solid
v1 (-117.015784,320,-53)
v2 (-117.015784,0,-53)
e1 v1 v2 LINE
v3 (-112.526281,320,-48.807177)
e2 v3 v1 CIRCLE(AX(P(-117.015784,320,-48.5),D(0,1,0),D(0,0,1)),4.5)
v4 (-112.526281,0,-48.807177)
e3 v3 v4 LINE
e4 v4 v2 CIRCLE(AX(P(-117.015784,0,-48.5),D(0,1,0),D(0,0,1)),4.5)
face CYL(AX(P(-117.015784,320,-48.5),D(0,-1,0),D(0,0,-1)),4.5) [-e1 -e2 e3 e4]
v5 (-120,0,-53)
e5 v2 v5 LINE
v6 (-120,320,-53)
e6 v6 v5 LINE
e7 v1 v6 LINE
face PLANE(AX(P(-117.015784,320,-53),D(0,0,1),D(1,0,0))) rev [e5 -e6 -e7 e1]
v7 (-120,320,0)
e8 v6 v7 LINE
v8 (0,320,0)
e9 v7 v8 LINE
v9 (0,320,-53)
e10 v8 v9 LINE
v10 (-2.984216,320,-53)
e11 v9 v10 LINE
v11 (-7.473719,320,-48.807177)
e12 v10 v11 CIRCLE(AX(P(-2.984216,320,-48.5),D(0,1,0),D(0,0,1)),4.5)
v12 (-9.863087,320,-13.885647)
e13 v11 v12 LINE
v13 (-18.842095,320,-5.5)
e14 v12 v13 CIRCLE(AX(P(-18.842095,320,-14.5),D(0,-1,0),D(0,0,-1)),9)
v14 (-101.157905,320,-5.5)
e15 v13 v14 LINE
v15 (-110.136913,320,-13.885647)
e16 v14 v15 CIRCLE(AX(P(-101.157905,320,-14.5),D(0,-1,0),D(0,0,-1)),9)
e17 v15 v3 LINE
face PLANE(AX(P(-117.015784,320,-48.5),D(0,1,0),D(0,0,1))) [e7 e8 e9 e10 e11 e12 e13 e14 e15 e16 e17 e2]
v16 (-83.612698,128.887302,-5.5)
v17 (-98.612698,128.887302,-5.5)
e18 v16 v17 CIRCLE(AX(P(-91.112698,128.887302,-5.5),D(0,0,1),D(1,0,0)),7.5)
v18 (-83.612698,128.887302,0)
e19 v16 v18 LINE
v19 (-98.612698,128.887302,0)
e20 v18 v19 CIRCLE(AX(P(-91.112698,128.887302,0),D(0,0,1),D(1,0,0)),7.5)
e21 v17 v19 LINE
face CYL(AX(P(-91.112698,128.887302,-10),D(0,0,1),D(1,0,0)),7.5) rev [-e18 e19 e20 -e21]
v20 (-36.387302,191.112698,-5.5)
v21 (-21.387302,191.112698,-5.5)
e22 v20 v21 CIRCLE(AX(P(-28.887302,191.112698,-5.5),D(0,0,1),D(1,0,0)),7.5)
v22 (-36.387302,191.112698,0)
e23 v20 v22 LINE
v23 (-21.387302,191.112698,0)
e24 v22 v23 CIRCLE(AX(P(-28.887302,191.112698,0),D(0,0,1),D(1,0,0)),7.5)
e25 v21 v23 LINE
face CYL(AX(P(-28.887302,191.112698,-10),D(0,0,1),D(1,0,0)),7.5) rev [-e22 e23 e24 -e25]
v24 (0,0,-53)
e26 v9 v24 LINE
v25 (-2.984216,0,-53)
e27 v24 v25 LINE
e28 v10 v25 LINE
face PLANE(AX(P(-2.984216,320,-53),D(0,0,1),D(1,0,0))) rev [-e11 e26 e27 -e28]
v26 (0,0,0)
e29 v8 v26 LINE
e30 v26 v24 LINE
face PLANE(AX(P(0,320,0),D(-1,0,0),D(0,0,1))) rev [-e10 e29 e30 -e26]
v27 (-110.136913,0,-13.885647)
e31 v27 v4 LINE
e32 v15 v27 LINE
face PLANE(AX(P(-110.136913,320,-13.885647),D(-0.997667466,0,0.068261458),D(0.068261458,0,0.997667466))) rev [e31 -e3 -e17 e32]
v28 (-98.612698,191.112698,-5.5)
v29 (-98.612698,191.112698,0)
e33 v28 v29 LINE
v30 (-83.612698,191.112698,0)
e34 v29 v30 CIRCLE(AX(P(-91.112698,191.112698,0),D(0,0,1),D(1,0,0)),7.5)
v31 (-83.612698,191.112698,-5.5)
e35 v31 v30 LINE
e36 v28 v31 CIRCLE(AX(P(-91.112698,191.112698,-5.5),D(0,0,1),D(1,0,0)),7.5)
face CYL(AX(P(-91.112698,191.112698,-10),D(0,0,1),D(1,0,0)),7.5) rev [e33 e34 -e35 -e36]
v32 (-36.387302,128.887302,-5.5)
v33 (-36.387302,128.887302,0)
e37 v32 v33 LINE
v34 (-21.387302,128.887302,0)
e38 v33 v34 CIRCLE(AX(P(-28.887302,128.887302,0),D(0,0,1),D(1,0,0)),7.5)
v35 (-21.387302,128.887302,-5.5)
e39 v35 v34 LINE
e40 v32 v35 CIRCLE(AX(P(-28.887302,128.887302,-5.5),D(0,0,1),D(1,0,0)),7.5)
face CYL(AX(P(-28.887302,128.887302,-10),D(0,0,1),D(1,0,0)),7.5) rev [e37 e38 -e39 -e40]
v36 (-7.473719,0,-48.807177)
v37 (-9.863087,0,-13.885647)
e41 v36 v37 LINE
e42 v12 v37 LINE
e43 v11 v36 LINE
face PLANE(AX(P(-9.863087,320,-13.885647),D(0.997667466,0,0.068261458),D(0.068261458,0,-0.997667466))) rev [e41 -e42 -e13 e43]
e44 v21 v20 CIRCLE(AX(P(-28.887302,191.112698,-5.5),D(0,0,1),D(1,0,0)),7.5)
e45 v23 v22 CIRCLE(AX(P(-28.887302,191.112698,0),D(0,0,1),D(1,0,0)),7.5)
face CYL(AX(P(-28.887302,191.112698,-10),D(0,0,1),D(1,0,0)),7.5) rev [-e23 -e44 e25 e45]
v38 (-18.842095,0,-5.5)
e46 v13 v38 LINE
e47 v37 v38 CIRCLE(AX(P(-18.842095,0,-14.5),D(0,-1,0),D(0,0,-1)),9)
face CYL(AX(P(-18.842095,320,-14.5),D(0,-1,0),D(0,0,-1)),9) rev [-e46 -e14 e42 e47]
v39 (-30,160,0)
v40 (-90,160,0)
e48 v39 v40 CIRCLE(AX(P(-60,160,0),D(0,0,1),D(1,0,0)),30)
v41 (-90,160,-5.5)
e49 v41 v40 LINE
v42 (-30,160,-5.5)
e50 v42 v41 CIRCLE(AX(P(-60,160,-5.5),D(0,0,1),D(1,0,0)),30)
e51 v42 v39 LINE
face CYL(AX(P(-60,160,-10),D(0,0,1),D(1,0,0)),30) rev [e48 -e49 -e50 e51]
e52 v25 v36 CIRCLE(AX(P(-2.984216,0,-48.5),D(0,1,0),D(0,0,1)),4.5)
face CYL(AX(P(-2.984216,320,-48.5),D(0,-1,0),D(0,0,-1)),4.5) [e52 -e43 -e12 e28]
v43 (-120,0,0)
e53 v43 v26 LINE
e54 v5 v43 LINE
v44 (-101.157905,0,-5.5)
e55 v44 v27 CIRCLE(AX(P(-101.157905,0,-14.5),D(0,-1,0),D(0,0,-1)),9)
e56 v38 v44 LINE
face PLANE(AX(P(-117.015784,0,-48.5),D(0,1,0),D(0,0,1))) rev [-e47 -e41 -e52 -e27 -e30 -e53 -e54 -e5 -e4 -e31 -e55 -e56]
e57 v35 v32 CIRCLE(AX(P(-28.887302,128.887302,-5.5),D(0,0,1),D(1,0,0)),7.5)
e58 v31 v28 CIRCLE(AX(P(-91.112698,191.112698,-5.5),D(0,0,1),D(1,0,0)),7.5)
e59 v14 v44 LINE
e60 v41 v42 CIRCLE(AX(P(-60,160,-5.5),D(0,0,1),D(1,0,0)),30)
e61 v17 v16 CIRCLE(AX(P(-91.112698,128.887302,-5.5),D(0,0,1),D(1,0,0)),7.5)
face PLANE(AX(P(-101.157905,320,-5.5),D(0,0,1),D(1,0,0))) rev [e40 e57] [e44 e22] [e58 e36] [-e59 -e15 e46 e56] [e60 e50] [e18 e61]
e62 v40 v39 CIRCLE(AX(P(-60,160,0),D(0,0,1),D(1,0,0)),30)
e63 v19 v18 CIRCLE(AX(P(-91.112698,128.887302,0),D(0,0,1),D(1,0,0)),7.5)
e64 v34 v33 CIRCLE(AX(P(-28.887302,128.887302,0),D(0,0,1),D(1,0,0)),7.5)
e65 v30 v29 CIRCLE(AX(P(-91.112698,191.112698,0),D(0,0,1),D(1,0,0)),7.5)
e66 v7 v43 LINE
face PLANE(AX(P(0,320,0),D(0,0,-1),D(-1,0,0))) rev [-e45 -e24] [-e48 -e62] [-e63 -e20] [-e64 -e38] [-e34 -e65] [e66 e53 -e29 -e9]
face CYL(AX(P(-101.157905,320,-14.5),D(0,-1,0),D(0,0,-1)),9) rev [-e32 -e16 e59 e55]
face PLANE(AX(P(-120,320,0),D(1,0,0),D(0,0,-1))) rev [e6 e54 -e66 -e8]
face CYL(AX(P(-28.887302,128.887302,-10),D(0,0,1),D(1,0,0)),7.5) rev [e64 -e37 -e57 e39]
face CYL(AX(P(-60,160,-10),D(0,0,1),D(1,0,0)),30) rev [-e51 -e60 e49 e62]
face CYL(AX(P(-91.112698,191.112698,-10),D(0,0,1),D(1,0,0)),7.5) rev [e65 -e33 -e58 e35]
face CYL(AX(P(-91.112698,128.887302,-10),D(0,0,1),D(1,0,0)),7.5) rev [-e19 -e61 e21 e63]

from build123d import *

# Parameters (mm, degrees)
MEMBER_12_1_DEPTH   = 320
SKETCH_5_R          = 30
SKETCH_5_R_2        = 7.5
CUT_EXTRUDE_1_DEPTH = 10


with BuildPart() as part:
    # Sketch1 → Member 12_1 (new body)
    with BuildSketch(Plane.ZX):
        with BuildLine():
            Line((0, 0), (0, -120))
            Line((0, -120), (-53, -120))
            Line((-53, -120), (-53, -117.0157841))
            ThreePointArc((-53, -117.0157841), (-51.788791155, -113.944326346), (-48.807176562, -112.526280502))
            Line((-48.807176562, -112.526280502), (-13.885646876, -110.136912681))
            ThreePointArc((-13.885646876, -110.136912681), (-7.922417689, -107.300820993), (-5.5, -101.157905484))
            Line((-5.5, -101.157905484), (-5.5, -18.842094516))
            ThreePointArc((-5.5, -18.842094516), (-7.922417689, -12.699179007), (-13.885646876, -9.863087319))
            Line((-13.885646876, -9.863087319), (-48.807176562, -7.473719498))
            ThreePointArc((-48.807176562, -7.473719498), (-51.788791155, -6.055673654), (-53, -2.9842159))
            Line((-53, -2.9842159), (-53, 0))
            Line((-53, 0), (0, 0))
        make_face()
    extrude(amount=MEMBER_12_1_DEPTH)

    # 草图5 → 切除-拉伸1 (cut)
    with BuildSketch(Plane.XY):
        with Locations((-60, 160)):
            Circle(SKETCH_5_R)
        with Locations((-91.112698372, 191.112698372)):
            Circle(SKETCH_5_R_2)
        with Locations((-28.887301628, 191.112698372)):
            Circle(SKETCH_5_R_2)
        with Locations((-28.887301628, 128.887301628)):
            Circle(SKETCH_5_R_2)
        with Locations((-91.112698372, 128.887301628)):
            Circle(SKETCH_5_R_2)
    extrude(amount=-CUT_EXTRUDE_1_DEPTH, mode=Mode.SUBTRACT)


solid = part.part
